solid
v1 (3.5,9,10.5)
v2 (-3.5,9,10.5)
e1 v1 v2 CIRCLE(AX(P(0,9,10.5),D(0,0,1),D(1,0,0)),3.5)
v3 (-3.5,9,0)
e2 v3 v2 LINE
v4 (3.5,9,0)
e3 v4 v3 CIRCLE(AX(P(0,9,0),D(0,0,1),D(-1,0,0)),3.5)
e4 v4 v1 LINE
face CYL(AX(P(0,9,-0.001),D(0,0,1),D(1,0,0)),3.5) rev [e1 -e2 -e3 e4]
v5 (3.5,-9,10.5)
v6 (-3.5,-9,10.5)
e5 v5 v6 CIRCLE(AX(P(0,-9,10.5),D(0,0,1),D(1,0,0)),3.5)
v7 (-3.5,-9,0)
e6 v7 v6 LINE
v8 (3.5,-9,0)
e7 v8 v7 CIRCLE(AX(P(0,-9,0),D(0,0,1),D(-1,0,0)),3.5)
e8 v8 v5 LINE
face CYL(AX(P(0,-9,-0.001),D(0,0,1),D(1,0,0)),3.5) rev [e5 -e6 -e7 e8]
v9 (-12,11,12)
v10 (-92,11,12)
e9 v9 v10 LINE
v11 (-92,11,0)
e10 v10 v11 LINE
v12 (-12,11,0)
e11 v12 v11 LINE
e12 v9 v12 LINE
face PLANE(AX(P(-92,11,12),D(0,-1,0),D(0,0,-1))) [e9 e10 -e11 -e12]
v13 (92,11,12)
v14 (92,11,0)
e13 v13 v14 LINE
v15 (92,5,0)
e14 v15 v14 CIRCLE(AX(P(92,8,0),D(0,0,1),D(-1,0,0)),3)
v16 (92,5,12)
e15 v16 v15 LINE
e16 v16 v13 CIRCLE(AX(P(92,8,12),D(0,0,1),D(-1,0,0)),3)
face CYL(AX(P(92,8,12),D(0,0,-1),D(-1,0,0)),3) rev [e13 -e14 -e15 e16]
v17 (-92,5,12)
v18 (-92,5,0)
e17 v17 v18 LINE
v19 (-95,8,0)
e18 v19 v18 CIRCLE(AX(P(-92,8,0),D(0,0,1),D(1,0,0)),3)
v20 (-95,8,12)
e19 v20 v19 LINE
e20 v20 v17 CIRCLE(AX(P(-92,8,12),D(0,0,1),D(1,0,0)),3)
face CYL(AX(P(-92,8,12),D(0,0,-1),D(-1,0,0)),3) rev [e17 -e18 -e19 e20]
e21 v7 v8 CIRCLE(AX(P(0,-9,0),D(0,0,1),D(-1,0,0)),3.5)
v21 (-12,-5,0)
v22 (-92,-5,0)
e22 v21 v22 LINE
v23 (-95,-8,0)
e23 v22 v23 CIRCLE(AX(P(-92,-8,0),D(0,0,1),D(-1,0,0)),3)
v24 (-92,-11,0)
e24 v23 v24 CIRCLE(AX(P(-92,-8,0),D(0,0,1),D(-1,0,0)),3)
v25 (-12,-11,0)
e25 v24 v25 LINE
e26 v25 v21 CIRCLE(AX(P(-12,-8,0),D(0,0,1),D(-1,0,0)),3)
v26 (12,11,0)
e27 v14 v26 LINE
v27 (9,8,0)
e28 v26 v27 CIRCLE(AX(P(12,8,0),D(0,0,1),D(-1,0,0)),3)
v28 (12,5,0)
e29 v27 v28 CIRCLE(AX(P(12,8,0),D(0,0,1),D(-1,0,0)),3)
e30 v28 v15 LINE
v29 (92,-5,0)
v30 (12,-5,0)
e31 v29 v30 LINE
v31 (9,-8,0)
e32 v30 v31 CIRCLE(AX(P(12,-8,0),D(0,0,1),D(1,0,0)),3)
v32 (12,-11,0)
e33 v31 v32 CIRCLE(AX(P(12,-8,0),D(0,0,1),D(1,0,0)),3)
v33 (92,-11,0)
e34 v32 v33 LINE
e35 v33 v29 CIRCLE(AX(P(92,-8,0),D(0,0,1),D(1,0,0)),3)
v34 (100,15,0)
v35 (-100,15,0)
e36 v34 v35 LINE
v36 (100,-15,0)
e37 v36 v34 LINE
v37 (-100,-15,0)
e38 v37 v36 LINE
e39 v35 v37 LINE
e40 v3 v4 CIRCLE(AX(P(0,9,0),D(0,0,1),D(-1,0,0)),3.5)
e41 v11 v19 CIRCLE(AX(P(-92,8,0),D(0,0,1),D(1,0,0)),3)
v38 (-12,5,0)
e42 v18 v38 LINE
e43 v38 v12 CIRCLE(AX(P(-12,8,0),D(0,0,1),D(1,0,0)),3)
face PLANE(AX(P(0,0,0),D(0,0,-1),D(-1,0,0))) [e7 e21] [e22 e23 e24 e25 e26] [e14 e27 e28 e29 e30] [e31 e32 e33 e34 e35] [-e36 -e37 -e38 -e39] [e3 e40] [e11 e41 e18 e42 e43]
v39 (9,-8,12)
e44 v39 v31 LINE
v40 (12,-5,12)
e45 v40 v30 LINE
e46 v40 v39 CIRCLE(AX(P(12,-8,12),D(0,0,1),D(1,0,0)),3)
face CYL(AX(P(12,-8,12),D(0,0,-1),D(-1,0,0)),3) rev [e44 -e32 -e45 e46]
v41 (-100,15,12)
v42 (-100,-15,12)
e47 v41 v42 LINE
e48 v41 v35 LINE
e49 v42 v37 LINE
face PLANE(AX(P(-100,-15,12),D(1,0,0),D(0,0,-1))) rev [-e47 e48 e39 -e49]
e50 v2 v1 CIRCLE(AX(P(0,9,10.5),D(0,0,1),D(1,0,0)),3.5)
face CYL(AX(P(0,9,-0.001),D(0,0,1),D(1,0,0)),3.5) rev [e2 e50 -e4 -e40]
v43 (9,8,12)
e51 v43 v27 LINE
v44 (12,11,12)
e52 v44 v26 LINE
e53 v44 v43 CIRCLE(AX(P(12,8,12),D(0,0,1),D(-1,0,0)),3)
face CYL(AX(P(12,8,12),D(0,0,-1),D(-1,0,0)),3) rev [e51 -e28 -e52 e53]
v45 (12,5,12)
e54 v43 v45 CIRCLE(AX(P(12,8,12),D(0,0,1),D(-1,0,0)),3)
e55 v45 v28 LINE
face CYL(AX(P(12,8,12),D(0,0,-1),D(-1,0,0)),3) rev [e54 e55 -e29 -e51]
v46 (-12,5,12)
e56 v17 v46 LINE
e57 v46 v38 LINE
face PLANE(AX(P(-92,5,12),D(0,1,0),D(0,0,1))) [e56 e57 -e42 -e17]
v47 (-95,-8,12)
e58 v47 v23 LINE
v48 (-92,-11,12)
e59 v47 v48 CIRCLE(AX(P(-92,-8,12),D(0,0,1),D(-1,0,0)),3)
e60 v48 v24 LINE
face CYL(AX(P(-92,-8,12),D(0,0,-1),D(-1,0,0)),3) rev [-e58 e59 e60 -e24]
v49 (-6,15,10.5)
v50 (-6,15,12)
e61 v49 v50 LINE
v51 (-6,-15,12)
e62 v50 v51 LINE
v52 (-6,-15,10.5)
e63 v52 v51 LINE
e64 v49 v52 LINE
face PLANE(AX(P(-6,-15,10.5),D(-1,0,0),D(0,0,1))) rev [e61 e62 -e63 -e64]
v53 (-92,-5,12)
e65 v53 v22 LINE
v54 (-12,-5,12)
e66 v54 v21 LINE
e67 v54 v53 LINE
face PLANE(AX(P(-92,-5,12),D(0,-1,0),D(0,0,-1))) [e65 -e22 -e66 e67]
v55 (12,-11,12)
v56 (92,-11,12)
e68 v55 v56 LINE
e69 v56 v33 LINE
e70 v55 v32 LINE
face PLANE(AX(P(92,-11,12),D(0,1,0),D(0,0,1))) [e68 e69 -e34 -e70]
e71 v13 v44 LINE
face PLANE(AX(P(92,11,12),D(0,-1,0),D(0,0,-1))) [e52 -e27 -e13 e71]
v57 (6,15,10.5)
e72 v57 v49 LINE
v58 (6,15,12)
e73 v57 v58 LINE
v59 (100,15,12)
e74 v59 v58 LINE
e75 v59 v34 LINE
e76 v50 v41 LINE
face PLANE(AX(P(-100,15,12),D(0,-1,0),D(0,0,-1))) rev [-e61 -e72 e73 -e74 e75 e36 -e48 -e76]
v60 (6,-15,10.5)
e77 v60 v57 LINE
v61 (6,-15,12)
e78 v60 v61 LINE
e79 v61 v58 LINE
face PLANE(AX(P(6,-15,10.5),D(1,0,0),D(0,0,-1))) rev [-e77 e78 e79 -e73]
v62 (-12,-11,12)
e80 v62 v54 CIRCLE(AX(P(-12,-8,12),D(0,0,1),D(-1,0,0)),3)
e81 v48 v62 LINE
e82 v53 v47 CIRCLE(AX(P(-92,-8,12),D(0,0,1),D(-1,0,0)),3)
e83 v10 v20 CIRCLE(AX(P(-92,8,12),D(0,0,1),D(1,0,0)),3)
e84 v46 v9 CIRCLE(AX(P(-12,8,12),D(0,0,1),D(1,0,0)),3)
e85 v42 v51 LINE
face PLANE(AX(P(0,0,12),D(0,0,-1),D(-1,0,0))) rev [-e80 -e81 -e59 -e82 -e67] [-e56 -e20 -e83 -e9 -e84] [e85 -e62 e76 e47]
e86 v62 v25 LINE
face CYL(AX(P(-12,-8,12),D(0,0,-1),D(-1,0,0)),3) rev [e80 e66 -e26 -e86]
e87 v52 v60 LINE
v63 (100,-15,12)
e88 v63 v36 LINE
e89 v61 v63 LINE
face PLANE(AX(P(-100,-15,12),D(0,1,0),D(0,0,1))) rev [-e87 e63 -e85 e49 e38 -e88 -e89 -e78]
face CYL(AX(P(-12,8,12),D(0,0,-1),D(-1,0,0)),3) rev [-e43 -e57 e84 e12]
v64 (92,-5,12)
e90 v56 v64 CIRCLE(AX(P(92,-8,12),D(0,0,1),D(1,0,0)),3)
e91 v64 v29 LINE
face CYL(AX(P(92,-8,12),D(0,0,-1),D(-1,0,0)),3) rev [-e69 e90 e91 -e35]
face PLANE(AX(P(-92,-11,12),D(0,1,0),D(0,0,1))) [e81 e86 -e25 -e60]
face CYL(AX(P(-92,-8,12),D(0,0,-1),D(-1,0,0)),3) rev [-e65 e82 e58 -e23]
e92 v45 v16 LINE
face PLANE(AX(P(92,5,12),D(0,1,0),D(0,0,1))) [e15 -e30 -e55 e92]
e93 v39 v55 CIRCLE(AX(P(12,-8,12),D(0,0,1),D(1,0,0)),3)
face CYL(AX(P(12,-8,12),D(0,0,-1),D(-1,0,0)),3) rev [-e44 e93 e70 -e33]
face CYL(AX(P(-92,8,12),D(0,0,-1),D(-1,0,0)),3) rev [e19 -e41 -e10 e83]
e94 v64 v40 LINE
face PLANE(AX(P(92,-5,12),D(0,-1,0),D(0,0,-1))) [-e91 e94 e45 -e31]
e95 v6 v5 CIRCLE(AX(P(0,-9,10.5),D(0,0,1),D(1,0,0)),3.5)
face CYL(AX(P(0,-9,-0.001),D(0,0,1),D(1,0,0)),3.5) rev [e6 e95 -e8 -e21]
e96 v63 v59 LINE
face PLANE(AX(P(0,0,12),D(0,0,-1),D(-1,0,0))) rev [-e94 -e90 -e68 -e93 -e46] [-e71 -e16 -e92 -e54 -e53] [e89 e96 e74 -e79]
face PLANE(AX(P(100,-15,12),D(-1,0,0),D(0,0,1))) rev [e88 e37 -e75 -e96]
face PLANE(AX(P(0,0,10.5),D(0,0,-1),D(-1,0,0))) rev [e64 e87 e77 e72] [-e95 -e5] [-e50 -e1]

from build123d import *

# Parameters (mm, degrees)
SKETCH_1_W          = 200
SKETCH_1_H          = 30
EXTRUDE_1_DEPTH     = 12
SKETCH_2_W          = 12
SKETCH_2_H          = 30
CUT_EXTRUDE_1_DEPTH = 1.5
CUT_EXTRUDE_2_REACH = 103.662
SKETCH_3_R          = 3.5


with BuildPart() as part:
    # 草图1 → 凸台-拉伸1 (new body)
    with BuildSketch(Plane.XY):
        Rectangle(SKETCH_1_W, SKETCH_1_H)
        with BuildLine():
            Line((-92, 11), (-12, 11))
            ThreePointArc((-12, 11), (-9, 8), (-12, 5))
            Line((-12, 5), (-92, 5))
            ThreePointArc((-92, 5), (-95, 8), (-92, 11))
        make_face(mode=Mode.SUBTRACT)
        with BuildLine():
            Line((-92, -11), (-12, -11))
            ThreePointArc((-12, -11), (-9, -8), (-12, -5))
            Line((-12, -5), (-92, -5))
            ThreePointArc((-92, -5), (-95, -8), (-92, -11))
        make_face(mode=Mode.SUBTRACT)
        with BuildLine():
            Line((92, 11), (12, 11))
            ThreePointArc((12, 11), (9, 8), (12, 5))
            Line((12, 5), (92, 5))
            ThreePointArc((92, 5), (95, 8), (92, 11))
        make_face(mode=Mode.SUBTRACT)
        with BuildLine():
            Line((92, -11), (12, -11))
            ThreePointArc((12, -11), (9, -8), (12, -5))
            Line((12, -5), (92, -5))
            ThreePointArc((92, -5), (95, -8), (92, -11))
        make_face(mode=Mode.SUBTRACT)
    extrude(amount=EXTRUDE_1_DEPTH)

    # 草图2 → 切除-拉伸1 (cut)
    with BuildSketch(Plane.XY.offset(12)):
        Rectangle(SKETCH_2_W, SKETCH_2_H)
    extrude(amount=-CUT_EXTRUDE_1_DEPTH, mode=Mode.SUBTRACT)

    # 草图3 → 切除-拉伸2 (cut, up to next)
    with BuildSketch(Plane.XY.offset(10.5), mode=Mode.PRIVATE) as cut_extrude_2_sk1:
        with Locations((0, 9)):
            Circle(SKETCH_3_R)
    cut_extrude_2_tool1 = extrude(cut_extrude_2_sk1.sketch, amount=-CUT_EXTRUDE_2_REACH, mode=Mode.PRIVATE) & part.part
    # 草图3 → 切除-拉伸2 (cut, up to next)
    with BuildSketch(Plane.XY.offset(10.5), mode=Mode.PRIVATE) as cut_extrude_2_sk2:
        with Locations((0, -9)):
            Circle(SKETCH_3_R)
    cut_extrude_2_tool2 = extrude(cut_extrude_2_sk2.sketch, amount=-CUT_EXTRUDE_2_REACH, mode=Mode.PRIVATE) & part.part
    add(cut_extrude_2_tool1.solids().sort_by_distance((0, 9, 10.5))[0], mode=Mode.SUBTRACT)
    add(cut_extrude_2_tool2.solids().sort_by_distance((0, -9, 10.5))[0], mode=Mode.SUBTRACT)


solid = part.part
